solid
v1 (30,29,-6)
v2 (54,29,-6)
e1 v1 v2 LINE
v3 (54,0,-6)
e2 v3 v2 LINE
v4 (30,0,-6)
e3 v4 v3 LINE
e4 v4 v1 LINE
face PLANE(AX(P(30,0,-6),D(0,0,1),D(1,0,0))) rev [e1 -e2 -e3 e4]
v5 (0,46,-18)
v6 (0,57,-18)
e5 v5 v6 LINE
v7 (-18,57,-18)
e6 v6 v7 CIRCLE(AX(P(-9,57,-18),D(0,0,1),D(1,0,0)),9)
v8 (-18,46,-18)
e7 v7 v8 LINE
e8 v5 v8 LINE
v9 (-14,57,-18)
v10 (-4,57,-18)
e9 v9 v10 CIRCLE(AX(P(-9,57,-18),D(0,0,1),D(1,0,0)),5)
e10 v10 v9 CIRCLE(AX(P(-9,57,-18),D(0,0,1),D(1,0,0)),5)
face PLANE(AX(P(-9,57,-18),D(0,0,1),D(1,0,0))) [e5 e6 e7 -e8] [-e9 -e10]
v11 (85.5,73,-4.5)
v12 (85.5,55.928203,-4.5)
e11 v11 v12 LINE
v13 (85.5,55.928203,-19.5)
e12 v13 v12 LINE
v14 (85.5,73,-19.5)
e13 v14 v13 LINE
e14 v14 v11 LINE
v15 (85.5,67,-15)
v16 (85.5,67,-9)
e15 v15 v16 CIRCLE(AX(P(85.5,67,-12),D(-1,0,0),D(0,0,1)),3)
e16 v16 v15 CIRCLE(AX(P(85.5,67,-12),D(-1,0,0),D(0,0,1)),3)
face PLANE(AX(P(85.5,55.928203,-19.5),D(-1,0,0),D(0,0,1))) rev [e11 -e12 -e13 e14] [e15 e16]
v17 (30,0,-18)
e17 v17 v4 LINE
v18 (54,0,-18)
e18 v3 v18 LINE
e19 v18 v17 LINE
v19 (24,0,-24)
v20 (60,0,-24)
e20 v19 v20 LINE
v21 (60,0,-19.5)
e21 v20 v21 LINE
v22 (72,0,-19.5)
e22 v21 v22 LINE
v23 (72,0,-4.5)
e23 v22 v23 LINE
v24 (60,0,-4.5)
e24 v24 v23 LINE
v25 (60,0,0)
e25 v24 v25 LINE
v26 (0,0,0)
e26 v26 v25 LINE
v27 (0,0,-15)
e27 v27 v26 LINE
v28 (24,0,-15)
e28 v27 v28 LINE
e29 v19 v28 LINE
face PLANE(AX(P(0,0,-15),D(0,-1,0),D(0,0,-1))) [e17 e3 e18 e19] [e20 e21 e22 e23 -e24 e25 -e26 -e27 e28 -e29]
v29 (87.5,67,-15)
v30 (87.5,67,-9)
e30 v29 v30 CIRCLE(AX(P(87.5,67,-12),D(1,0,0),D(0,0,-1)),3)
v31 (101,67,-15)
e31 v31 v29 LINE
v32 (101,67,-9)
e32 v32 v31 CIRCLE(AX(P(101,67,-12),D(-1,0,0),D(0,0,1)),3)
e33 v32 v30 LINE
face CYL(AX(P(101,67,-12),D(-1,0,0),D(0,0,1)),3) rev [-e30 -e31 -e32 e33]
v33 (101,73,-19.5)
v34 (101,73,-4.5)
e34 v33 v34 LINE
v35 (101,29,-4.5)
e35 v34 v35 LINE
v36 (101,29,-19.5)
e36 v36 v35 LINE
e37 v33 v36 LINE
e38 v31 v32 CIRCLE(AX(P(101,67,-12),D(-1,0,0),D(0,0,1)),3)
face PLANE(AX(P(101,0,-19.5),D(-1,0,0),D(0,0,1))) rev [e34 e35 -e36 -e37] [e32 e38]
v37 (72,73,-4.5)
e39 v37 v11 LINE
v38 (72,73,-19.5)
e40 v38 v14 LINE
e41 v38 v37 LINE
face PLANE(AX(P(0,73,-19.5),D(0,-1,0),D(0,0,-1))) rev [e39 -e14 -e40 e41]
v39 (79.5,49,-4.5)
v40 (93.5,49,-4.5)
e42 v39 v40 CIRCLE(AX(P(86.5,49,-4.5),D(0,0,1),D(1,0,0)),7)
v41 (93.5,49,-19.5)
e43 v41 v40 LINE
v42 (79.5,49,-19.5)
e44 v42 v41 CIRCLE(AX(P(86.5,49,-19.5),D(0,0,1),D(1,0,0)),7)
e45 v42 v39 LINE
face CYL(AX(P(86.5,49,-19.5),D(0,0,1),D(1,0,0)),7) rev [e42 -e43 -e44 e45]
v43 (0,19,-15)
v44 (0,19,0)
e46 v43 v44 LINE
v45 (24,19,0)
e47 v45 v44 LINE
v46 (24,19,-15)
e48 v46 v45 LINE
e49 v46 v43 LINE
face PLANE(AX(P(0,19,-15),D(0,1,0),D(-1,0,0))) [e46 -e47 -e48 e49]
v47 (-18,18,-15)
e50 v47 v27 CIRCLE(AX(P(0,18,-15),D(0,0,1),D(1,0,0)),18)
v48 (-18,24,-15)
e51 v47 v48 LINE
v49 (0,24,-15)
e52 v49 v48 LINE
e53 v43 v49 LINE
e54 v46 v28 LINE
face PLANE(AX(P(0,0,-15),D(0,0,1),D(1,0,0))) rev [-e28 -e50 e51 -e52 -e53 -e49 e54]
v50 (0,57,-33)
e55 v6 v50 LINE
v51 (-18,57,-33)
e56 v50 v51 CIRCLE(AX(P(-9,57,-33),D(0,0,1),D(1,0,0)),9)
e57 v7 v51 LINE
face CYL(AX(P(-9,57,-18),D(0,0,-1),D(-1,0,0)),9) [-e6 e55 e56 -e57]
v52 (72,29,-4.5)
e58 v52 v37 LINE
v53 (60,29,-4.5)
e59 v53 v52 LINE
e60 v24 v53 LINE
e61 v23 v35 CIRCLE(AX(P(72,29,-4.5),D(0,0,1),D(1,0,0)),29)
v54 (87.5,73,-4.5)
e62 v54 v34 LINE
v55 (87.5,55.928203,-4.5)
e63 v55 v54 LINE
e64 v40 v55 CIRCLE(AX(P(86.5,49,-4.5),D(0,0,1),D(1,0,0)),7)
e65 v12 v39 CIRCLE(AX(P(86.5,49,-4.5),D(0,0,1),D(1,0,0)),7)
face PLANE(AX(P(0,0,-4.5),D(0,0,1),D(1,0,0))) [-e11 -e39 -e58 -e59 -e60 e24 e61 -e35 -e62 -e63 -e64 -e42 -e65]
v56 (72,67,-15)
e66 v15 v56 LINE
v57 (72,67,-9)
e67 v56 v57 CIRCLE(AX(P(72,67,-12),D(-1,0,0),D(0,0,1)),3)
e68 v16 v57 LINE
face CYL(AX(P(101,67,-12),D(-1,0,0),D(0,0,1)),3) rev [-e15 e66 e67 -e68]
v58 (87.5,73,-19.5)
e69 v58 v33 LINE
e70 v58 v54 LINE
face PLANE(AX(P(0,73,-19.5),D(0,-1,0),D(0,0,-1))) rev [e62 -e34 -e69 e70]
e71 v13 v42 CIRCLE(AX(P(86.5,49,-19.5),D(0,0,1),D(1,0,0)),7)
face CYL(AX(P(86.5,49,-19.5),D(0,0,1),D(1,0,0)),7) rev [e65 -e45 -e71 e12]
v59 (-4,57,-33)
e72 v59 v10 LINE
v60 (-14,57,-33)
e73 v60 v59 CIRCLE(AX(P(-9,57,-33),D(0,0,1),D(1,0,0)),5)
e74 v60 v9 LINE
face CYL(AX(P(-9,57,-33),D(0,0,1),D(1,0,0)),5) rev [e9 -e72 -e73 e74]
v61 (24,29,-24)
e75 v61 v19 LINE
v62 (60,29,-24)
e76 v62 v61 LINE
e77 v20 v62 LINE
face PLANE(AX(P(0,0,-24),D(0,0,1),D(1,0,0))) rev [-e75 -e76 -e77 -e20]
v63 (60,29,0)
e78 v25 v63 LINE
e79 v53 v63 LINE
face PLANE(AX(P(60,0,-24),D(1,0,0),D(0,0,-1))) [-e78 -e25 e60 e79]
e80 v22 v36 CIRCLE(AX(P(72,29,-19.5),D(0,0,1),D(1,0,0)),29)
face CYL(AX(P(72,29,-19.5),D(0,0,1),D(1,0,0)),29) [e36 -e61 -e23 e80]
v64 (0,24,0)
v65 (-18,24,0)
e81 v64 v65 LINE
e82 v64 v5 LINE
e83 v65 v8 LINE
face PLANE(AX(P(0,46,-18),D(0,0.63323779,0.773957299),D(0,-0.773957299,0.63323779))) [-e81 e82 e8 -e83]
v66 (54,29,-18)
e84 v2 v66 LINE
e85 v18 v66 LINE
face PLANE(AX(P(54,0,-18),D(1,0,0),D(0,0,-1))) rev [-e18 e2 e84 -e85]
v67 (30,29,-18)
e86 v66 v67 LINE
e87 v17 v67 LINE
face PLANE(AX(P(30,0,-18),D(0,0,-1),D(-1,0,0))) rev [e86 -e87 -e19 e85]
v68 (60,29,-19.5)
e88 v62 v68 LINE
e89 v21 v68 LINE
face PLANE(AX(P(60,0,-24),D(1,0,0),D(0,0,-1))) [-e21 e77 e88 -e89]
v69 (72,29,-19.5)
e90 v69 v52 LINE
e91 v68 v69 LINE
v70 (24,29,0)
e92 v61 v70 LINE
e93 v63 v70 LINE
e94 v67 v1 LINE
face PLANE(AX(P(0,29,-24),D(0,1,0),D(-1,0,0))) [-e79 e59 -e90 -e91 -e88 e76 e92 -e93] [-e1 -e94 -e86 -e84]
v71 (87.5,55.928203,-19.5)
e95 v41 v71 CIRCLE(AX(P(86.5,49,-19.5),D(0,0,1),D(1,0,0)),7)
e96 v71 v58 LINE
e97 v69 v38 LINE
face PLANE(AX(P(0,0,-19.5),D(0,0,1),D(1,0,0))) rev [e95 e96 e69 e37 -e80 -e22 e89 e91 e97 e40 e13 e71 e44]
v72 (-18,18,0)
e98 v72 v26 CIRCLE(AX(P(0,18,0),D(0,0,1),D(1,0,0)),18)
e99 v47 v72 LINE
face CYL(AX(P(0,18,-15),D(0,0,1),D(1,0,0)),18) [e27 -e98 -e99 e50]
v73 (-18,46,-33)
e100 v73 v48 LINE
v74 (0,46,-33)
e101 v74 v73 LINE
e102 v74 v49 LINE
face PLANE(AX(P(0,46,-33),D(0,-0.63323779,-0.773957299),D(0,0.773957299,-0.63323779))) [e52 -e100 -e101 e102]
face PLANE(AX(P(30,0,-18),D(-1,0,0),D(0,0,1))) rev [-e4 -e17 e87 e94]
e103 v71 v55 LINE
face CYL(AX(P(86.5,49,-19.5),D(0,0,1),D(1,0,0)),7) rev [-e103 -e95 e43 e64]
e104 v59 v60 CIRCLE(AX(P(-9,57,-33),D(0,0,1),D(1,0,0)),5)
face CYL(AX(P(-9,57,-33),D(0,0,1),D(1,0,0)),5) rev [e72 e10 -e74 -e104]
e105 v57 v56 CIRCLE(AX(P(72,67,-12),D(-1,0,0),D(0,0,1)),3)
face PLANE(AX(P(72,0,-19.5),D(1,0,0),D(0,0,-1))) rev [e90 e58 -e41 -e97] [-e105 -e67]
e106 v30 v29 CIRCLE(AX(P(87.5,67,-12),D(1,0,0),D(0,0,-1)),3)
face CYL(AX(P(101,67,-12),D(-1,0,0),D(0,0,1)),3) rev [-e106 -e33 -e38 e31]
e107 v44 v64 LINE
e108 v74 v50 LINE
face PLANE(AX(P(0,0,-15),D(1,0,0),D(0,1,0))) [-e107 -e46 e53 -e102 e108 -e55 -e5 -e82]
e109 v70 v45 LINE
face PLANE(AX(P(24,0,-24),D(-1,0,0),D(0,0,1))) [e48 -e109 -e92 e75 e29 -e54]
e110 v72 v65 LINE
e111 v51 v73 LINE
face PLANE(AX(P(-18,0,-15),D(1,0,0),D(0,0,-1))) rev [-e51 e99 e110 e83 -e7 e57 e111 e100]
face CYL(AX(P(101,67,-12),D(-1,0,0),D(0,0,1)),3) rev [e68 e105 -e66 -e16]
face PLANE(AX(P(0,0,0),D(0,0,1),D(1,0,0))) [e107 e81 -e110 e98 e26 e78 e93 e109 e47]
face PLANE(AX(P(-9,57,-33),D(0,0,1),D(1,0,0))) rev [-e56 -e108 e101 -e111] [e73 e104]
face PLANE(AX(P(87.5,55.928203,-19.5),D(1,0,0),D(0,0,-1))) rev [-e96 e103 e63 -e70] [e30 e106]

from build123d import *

# Parameters (mm, degrees)
Z_PROFILE_PLATE_DEPTH       = 15
ARM_EXTENSION_BOSS_DEPTH    = 24
CLAMP_START                 = -4.5
CLAMP_HUB_BOSS_DEPTH        = 15
CENTER_BLOCK_DEPTH          = 18
PIVOT_START                 = -1.5
PIVOT_LUG_DEPTH             = 7.5
PIVOT_HOLE_SKETCH_R         = 5
PIVOT_HOLE_10_DEPTH         = 15
RECTANGULAR_POCKET_SKETCH_W = 24
RECTANGULAR_POCKET_SKETCH_H = 12
RECTANGULAR_POCKET_DEPTH    = 116.004347744
CLAMP_SLOT_DEPTH            = 15
CLAMP_SCREW_HOLE_SKETCH_R   = 3
CLAMP_SCREW_HOLE_6_DEPTH    = 121.490663539


with BuildPart() as part:
    # Z Profile Sketch → Z Profile Plate (new body)
    with BuildSketch(Plane.XY):
        with BuildLine():
            ThreePointArc((-18, 18), (-12.727922061, 5.272077939), (0, 0))
            Line((0, 0), (24, 0))
            Line((24, 0), (24, 19))
            Line((24, 19), (0, 19))
            Line((0, 19), (0, 24))
            Line((0, 24), (-16.970562748, 24))
            Line((-16.970562748, 24), (-18, 24))
            Line((-18, 24), (-18, 18))
        make_face()
    extrude(amount=-Z_PROFILE_PLATE_DEPTH)

    # Sketch1_6 → Arm Extension Boss (add)
    with BuildSketch(Plane.XY):
        Polygon((24, 19), (24, 0), (60, 0), (60, 29), (24, 29), align=None)
    extrude(amount=-ARM_EXTENSION_BOSS_DEPTH)

    # Sketch1_7 → Clamp Hub Boss (add)
    with BuildSketch(Plane.XY.offset(CLAMP_START)):
        with BuildLine():
            Line((60, 0), (72, 0))
            ThreePointArc((72, 0), (92.506096654, 8.493903346), (101, 29))
            Line((101, 29), (101, 73))
            Line((101, 73), (72, 73))
            Line((72, 73), (72, 29))
            Line((72, 29), (60, 29))
            Line((60, 29), (60, 0))
        make_face()
    extrude(amount=-CLAMP_HUB_BOSS_DEPTH)

    # Center Block Sketch → Center Block (add)
    with BuildSketch(Plane.ZY.offset(18)):
        Polygon((-33, 46), (-15, 24), (0, 24), (-18, 46), align=None)
    extrude(amount=-CENTER_BLOCK_DEPTH)

    # Pivot Lug Sketch → Pivot Lug (add, symmetric)
    with BuildSketch(Plane.XY.offset(-24).offset(PIVOT_START)):
        with BuildLine():
            Line((-18, 57), (-18, 46))
            Line((-18, 46), (0, 46))
            Line((0, 46), (0, 57))
            ThreePointArc((0, 57), (-9, 66), (-18, 57))
        make_face()
    extrude(amount=PIVOT_LUG_DEPTH, both=True)

    # Pivot Hole Sketch → Pivot Hole _10 (cut)
    with BuildSketch(Plane.XY.offset(-18)):
        with Locations((-9, 57)):
            Circle(PIVOT_HOLE_SKETCH_R)
    extrude(amount=-PIVOT_HOLE_10_DEPTH, mode=Mode.SUBTRACT)

    # Rectangular Pocket Sketch → Rectangular Pocket (cut, through all)
    with BuildSketch(Plane(origin=(0, 29, 0), x_dir=(1, 0, 0), z_dir=(0, 1, 0))):
        with Locations((42, 12)):
            Rectangle(RECTANGULAR_POCKET_SKETCH_W, RECTANGULAR_POCKET_SKETCH_H)
    extrude(amount=-RECTANGULAR_POCKET_DEPTH, mode=Mode.SUBTRACT)

    # Clamp Slot Sketch → Clamp Slot (cut)
    with BuildSketch(Plane.XY.offset(-4.5)):
        with BuildLine():
            Line((87.5, 55.92820323), (87.5, 73))
            Line((87.5, 73), (85.5, 73))
            Line((85.5, 73), (85.5, 55.92820323))
            ThreePointArc((85.5, 55.92820323), (86.5, 42), (87.5, 55.92820323))
        make_face()
    extrude(amount=-CLAMP_SLOT_DEPTH, mode=Mode.SUBTRACT)

    # Clamp Screw Hole Sketch → Clamp Screw Hole _6 (cut, through all)
    with BuildSketch(Plane.ZY.offset(-72)):
        with Locations((-12, 67)):
            Circle(CLAMP_SCREW_HOLE_SKETCH_R)
    extrude(amount=-CLAMP_SCREW_HOLE_6_DEPTH, mode=Mode.SUBTRACT)


solid = part.part
